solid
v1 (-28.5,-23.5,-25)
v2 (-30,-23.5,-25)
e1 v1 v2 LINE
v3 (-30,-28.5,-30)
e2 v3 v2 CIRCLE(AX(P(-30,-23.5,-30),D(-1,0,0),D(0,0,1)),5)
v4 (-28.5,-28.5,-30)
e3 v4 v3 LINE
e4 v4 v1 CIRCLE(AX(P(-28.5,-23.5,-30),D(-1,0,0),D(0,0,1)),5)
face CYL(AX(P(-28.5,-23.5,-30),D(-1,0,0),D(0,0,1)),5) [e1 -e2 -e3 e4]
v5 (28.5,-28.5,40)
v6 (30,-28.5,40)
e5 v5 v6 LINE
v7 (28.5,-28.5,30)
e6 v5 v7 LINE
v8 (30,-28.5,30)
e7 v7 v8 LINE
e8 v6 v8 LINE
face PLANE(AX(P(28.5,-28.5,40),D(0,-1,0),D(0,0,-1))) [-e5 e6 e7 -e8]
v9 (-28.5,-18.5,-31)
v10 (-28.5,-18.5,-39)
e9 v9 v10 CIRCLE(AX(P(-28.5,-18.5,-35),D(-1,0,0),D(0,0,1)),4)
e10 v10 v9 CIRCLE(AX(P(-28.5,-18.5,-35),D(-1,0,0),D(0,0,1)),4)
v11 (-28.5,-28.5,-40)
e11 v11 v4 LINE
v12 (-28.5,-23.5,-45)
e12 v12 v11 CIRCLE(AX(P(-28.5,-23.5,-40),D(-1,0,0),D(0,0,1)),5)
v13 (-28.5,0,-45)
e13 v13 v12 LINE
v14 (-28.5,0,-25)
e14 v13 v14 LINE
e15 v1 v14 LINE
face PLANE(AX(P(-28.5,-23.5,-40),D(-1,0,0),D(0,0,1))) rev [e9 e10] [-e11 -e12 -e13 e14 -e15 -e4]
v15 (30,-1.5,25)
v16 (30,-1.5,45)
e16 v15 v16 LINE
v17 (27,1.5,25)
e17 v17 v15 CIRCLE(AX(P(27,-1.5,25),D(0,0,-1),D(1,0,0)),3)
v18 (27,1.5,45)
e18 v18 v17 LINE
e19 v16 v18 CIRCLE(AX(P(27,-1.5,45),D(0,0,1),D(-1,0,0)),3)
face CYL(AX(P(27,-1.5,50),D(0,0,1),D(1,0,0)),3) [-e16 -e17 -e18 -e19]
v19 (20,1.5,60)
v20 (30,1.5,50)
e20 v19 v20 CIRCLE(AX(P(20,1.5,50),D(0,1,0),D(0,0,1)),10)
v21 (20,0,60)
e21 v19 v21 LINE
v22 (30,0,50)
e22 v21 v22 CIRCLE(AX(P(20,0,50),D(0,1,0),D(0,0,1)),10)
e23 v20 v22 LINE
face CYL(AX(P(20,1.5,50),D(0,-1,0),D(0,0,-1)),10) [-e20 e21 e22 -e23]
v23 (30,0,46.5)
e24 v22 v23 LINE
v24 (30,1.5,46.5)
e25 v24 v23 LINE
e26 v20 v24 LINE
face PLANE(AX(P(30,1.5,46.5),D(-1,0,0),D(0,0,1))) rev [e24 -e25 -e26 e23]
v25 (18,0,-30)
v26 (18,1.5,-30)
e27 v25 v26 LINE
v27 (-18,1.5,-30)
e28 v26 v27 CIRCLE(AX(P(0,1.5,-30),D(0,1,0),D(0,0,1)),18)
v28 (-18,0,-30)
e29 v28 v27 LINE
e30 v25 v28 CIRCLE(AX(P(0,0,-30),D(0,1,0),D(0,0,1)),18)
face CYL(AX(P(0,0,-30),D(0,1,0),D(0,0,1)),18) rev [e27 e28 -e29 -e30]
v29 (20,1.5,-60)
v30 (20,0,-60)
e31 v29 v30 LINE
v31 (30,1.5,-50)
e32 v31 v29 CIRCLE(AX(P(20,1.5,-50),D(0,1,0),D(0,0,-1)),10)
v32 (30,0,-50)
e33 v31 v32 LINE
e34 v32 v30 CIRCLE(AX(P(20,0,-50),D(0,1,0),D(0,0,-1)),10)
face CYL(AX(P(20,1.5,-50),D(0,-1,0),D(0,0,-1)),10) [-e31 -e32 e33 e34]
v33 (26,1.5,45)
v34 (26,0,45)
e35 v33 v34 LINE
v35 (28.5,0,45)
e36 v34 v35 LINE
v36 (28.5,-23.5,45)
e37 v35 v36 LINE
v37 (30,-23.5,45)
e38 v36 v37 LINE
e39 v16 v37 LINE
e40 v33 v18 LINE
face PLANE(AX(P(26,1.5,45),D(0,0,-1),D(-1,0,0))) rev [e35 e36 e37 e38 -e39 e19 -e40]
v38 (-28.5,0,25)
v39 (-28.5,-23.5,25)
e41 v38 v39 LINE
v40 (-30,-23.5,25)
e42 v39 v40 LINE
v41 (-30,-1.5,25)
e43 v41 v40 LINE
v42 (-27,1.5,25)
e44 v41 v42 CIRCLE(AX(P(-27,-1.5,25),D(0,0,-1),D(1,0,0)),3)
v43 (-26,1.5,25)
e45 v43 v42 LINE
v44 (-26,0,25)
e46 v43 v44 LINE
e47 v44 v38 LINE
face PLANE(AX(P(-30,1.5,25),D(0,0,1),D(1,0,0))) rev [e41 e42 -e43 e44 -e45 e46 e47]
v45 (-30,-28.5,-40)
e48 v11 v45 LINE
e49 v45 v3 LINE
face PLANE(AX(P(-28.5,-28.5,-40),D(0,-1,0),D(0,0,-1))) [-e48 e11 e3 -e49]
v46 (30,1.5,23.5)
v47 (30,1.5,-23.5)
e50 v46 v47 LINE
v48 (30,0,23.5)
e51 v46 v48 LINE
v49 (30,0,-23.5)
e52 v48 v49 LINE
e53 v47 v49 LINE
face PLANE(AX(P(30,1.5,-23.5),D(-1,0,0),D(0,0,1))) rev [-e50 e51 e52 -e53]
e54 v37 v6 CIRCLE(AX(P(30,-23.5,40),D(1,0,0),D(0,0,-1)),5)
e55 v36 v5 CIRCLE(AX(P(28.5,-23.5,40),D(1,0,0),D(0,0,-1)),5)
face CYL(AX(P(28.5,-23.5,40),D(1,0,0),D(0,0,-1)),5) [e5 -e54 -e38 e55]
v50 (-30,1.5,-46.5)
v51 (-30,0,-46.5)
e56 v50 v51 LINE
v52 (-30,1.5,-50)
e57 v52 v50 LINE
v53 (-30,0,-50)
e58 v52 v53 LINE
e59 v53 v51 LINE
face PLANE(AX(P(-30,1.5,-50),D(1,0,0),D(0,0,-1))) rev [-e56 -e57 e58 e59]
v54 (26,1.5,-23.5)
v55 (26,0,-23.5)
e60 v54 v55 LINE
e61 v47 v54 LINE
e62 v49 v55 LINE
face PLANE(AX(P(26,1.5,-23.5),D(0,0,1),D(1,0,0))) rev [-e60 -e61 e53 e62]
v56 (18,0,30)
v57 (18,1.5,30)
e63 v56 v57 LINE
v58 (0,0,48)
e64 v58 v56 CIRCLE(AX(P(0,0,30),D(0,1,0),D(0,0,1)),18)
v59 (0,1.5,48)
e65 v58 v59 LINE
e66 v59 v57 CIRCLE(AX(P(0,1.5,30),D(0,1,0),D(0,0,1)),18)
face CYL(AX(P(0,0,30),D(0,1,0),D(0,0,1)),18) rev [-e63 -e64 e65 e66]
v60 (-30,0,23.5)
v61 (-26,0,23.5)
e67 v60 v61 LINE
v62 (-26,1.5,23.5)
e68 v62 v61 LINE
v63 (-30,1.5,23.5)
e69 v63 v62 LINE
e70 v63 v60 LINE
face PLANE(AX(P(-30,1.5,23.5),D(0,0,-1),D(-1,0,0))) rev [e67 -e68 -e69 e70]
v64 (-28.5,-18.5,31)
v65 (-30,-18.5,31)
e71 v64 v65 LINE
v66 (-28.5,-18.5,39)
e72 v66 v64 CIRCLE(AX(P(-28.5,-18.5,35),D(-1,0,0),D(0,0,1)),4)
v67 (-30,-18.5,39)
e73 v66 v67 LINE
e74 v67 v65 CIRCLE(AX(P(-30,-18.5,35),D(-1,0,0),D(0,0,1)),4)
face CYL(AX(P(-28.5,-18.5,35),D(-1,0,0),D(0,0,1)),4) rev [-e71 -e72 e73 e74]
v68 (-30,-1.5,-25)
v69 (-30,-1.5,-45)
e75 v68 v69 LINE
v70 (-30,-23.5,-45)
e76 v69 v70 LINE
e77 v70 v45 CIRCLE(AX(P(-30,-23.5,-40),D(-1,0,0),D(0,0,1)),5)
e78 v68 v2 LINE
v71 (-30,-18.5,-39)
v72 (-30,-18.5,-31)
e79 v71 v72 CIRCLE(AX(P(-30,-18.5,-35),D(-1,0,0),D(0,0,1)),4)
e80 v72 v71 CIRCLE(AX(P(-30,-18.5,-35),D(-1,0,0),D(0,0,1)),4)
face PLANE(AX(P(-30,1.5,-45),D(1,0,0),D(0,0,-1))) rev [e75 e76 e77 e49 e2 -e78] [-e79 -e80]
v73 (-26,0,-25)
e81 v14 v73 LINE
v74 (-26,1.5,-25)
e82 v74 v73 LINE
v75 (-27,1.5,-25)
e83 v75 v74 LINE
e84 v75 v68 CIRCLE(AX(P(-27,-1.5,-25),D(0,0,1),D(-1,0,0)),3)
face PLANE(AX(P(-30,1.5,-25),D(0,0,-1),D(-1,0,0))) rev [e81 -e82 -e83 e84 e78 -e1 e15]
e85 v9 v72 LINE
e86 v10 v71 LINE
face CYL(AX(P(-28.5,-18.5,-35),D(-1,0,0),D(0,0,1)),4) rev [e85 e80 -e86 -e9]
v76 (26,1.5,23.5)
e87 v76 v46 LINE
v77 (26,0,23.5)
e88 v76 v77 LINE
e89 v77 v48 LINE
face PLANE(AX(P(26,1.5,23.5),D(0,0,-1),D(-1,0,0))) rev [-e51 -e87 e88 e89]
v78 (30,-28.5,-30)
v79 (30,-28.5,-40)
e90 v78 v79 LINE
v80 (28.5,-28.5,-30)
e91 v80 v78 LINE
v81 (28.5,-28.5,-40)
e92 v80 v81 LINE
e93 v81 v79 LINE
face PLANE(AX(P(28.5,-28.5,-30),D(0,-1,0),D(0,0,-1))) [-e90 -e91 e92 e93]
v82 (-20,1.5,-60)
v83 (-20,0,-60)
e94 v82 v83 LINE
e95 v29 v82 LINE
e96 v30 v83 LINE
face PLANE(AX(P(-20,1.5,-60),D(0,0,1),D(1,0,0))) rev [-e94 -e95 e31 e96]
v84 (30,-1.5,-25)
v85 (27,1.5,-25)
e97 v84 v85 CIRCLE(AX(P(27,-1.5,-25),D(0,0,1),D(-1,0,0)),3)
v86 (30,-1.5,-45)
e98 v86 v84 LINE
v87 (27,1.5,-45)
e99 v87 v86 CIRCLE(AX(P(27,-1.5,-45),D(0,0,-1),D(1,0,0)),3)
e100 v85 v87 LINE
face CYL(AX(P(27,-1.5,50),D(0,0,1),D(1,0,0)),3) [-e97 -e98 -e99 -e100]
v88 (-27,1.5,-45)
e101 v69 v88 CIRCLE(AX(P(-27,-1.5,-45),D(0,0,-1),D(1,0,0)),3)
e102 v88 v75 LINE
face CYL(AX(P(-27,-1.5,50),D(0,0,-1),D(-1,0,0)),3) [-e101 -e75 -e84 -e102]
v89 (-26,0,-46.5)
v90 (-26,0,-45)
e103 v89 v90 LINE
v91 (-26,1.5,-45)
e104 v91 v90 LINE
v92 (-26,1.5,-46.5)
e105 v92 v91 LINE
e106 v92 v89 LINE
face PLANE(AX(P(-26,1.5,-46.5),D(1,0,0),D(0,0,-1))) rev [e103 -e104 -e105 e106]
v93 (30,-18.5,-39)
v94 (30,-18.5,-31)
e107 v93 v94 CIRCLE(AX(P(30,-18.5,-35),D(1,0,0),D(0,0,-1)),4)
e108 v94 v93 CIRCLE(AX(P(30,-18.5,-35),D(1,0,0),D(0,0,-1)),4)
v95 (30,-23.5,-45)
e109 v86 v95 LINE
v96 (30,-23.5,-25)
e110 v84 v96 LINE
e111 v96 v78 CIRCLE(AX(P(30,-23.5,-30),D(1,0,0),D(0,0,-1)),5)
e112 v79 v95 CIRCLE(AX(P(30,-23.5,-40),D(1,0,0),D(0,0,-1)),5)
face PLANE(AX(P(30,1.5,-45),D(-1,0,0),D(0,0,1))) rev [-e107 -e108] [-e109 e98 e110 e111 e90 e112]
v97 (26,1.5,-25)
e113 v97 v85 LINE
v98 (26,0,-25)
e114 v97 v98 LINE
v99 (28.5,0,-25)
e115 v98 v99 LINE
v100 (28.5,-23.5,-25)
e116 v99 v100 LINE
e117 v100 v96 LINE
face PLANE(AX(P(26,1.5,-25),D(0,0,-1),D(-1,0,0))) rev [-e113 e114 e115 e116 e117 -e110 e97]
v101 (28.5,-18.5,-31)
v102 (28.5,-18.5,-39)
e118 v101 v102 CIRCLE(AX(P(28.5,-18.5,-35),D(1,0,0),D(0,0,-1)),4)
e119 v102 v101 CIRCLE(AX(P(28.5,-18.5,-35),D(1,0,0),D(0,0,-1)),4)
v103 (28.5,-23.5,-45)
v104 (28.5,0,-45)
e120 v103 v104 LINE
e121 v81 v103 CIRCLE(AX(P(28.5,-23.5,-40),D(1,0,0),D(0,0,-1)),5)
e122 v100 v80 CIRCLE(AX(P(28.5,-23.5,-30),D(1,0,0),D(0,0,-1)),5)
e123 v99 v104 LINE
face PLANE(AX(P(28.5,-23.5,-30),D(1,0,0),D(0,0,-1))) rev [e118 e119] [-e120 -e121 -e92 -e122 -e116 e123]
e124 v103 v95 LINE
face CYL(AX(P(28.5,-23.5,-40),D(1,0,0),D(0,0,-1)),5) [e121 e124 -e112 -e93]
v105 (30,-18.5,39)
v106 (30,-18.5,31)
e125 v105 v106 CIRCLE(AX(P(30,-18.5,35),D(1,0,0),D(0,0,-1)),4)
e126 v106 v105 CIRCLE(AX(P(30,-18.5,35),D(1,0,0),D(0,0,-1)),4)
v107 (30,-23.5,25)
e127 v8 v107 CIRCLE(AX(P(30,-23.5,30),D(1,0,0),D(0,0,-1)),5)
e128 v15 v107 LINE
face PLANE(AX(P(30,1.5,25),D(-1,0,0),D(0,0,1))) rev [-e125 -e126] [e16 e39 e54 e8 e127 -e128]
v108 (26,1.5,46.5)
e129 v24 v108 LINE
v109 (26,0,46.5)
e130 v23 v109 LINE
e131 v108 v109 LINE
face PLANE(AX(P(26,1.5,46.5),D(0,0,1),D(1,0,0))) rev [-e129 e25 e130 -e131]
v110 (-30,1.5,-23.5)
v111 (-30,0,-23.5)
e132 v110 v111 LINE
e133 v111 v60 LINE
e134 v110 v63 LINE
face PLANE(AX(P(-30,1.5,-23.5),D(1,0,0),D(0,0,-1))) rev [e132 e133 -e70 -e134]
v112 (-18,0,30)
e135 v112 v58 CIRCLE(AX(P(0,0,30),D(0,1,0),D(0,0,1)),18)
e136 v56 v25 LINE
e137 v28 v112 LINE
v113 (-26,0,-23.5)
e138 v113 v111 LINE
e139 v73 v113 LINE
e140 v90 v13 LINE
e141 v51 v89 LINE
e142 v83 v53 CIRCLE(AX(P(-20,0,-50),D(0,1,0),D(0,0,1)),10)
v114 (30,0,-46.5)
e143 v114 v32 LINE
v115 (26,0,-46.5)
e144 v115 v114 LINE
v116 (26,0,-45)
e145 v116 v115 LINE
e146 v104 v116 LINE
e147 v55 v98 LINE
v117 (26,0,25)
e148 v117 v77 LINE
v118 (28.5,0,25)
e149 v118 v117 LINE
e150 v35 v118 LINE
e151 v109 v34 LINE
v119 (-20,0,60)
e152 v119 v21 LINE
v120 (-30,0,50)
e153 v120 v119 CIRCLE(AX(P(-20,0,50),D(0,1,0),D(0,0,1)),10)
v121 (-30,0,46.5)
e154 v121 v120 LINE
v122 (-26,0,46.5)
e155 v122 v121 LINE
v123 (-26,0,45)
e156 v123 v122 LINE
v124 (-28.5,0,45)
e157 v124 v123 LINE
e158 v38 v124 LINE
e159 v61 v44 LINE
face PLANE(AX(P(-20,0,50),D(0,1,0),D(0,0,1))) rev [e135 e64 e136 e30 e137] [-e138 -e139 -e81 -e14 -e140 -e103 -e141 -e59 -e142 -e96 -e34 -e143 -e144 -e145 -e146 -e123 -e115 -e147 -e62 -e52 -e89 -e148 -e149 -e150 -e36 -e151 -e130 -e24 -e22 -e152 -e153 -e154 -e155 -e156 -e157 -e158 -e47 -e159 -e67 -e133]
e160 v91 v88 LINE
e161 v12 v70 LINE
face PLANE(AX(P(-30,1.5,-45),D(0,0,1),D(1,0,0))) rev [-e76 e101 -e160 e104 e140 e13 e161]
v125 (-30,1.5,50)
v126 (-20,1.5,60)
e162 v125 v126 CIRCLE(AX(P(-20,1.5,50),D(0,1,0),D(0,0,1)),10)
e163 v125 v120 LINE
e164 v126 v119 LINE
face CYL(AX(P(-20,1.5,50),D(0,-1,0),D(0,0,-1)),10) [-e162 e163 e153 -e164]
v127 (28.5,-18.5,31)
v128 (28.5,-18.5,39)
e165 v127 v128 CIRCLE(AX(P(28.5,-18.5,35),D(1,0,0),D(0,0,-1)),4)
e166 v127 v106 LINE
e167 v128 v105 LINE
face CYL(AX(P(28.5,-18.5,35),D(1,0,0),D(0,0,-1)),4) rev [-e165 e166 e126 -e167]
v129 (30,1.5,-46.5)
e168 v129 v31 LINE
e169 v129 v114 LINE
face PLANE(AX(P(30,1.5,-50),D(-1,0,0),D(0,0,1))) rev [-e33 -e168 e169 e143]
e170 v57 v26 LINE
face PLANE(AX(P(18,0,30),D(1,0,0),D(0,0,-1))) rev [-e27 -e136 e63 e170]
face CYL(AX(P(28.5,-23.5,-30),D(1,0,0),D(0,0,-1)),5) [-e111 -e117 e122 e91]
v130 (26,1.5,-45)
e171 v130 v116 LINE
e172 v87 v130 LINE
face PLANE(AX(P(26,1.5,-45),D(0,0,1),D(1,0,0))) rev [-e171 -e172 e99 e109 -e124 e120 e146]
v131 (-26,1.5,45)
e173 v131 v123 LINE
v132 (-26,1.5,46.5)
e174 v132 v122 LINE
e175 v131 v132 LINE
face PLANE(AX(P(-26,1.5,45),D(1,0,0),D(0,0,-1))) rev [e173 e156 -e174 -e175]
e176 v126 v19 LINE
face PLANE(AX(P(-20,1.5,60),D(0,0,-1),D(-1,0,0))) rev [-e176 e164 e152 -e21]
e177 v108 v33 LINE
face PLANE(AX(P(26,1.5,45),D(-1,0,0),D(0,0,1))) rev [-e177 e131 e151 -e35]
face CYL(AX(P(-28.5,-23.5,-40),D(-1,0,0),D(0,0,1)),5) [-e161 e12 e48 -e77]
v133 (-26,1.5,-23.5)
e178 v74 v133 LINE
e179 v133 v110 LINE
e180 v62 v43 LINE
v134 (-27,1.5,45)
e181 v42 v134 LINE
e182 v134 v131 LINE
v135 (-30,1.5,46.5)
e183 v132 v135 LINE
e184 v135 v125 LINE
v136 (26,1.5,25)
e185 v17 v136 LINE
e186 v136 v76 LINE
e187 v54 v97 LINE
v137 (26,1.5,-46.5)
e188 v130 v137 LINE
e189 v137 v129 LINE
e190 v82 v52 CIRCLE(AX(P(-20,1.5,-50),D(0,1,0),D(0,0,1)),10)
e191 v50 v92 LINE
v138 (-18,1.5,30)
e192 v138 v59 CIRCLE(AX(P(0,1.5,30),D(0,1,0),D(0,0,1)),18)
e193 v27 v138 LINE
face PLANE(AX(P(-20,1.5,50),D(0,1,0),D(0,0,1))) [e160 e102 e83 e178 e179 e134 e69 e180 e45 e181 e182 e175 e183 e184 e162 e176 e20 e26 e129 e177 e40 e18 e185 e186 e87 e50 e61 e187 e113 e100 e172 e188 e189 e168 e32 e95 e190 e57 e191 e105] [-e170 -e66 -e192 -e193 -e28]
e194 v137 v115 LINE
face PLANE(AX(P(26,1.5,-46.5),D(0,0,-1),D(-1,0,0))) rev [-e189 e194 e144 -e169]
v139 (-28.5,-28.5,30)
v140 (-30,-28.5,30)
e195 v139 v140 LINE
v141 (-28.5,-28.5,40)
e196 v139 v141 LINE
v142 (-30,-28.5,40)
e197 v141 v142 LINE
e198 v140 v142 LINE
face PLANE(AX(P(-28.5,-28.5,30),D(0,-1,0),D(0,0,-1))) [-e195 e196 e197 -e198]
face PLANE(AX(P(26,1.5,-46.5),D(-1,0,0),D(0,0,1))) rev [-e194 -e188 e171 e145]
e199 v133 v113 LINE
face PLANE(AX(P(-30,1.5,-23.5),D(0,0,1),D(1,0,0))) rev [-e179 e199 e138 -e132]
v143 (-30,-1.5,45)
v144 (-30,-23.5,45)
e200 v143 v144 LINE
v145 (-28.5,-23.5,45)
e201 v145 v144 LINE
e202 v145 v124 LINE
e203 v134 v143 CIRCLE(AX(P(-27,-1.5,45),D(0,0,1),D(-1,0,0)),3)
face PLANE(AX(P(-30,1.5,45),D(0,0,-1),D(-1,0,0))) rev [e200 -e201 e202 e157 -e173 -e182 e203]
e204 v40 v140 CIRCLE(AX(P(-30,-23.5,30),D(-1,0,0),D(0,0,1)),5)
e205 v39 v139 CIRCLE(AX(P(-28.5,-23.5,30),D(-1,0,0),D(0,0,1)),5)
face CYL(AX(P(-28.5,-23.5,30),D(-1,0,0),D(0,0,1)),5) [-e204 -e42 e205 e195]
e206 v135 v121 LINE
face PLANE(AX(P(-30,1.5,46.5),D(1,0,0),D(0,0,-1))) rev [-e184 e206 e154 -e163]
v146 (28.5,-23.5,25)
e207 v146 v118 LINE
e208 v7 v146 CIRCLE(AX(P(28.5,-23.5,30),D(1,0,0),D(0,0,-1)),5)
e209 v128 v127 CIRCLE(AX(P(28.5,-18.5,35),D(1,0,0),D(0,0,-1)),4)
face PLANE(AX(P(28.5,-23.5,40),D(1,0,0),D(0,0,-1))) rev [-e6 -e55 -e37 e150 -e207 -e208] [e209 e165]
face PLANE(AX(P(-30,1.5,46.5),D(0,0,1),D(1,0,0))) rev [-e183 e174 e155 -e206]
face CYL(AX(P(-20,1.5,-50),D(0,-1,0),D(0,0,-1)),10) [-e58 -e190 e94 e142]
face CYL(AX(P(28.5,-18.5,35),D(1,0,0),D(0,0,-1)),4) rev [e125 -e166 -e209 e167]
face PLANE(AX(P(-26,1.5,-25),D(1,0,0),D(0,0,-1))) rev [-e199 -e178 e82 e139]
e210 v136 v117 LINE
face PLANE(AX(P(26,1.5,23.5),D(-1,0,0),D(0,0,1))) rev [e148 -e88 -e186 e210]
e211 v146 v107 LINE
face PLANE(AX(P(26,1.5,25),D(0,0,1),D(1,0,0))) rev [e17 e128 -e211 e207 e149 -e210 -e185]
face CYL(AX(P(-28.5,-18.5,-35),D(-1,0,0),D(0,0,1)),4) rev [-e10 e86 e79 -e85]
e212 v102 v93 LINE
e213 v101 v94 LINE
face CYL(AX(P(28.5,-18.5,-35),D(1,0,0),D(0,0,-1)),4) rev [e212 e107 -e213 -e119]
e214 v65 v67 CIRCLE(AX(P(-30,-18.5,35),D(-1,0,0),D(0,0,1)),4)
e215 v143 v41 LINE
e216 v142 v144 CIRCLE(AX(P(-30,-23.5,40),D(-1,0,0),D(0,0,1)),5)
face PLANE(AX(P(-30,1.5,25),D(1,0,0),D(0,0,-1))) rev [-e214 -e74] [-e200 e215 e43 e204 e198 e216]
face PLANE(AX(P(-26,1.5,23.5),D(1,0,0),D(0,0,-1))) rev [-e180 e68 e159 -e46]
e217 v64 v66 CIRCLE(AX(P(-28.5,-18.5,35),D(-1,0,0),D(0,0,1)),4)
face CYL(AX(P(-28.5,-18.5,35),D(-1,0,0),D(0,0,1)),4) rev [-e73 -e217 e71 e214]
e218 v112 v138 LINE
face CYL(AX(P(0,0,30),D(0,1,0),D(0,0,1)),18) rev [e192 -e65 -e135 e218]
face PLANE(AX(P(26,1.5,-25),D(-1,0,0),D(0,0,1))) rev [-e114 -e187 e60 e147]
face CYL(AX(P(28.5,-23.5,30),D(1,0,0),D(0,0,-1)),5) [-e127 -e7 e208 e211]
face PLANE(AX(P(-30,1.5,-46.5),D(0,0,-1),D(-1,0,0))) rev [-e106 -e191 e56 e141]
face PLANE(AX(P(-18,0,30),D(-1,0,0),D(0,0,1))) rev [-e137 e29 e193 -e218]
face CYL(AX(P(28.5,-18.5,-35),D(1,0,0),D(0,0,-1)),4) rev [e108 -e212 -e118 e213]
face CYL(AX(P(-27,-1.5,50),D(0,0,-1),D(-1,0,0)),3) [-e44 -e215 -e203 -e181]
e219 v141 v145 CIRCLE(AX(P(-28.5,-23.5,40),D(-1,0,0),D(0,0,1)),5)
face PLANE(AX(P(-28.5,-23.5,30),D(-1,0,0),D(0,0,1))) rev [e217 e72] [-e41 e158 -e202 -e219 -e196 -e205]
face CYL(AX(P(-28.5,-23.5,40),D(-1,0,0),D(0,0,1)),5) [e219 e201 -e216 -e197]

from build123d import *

# Parameters (mm, degrees)
COVER_PLATE_1_5MM_DEPTH    = 1.5
SIDE_A_LEGS_SKETCH_R       = 4
SIDE_A_MOUNTING_LEGS_DEPTH = 1.5
SIDE_START                 = -1.5
SIDE_B_LEGS_SKETCH_R       = 4
SIDE_B_MOUNTING_LEGS_DEPTH = 1.5
CORNER_FILLETS_R3_R        = 3
OBLONG_SLOT_CUT_DEPTH      = 1.5


with BuildPart() as part:
    # Cover Plate Sketch → Cover Plate 1.5mm (new body)
    with BuildSketch(Plane(origin=(0, 0, 0), x_dir=(1, 0, 0), z_dir=(0, 1, 0))):
        with BuildLine():
            Line((-30, 45), (-26, 45))
            Line((-26, 45), (-26, 46.5))
            Line((-26, 46.5), (-30, 46.5))
            Line((-30, 46.5), (-30, 50))
            ThreePointArc((-30, 50), (-27.071067812, 57.071067812), (-20, 60))
            Line((-20, 60), (20, 60))
            ThreePointArc((20, 60), (27.071067812, 57.071067812), (30, 50))
            Line((30, 50), (30, 46.5))
            Line((30, 46.5), (26, 46.5))
            Line((26, 46.5), (26, 45))
            Line((26, 45), (30, 45))
            Line((30, 45), (30, 25))
            Line((30, 25), (26, 25))
            Line((26, 25), (26, 23.5))
            Line((26, 23.5), (30, 23.5))
            Line((30, 23.5), (30, -23.5))
            Line((30, -23.5), (26, -23.5))
            Line((26, -23.5), (26, -25))
            Line((26, -25), (30, -25))
            Line((30, -25), (30, -45))
            Line((30, -45), (26, -45))
            Line((26, -45), (26, -46.5))
            Line((26, -46.5), (30, -46.5))
            Line((30, -46.5), (30, -50))
            ThreePointArc((30, -50), (27.071067812, -57.071067812), (20, -60))
            Line((20, -60), (-20, -60))
            ThreePointArc((-20, -60), (-27.071067812, -57.071067812), (-30, -50))
            Line((-30, -50), (-30, -46.5))
            Line((-30, -46.5), (-26, -46.5))
            Line((-26, -46.5), (-26, -45))
            Line((-26, -45), (-30, -45))
            Line((-30, -45), (-30, -25))
            Line((-30, -25), (-26, -25))
            Line((-26, -25), (-26, -23.5))
            Line((-26, -23.5), (-30, -23.5))
            Line((-30, -23.5), (-30, 23.5))
            Line((-30, 23.5), (-26, 23.5))
            Line((-26, 23.5), (-26, 25))
            Line((-26, 25), (-30, 25))
            Line((-30, 25), (-30, 45))
        make_face()
    extrude(amount=COVER_PLATE_1_5MM_DEPTH)

    # Side A Legs Sketch → Side A Mounting Legs (add)
    # profile 1 of 2: a face of its own
    with BuildSketch(Plane(origin=(30, 0, 0), x_dir=(0, 0, -1), z_dir=(1, 0, 0))):
        with BuildLine():
            Line((-45, 1.5), (-25, 1.5))
            Line((-25, 1.5), (-25, -23.5))
            ThreePointArc((-25, -23.5), (-26.464466094, -27.035533906), (-30, -28.5))
            Line((-30, -28.5), (-40, -28.5))
            ThreePointArc((-40, -28.5), (-43.535533906, -27.035533906), (-45, -23.5))
            Line((-45, -23.5), (-45, 1.5))
        make_face()
        with Locations((-35, -18.5)):
            Circle(SIDE_A_LEGS_SKETCH_R, mode=Mode.SUBTRACT)
    # profile 2 of 2: a face of its own
    with BuildSketch(Plane(origin=(30, 0, 0), x_dir=(0, 0, -1), z_dir=(1, 0, 0))):
        with BuildLine():
            Line((25, 1.5), (45, 1.5))
            Line((45, 1.5), (45, -23.5))
            ThreePointArc((45, -23.5), (43.535533906, -27.035533906), (40, -28.5))
            Line((40, -28.5), (30, -28.5))
            ThreePointArc((30, -28.5), (26.464466094, -27.035533906), (25, -23.5))
            Line((25, -23.5), (25, 1.5))
        make_face()
        with Locations((35, -18.5)):
            Circle(SIDE_A_LEGS_SKETCH_R, mode=Mode.SUBTRACT)
    extrude(amount=-SIDE_A_MOUNTING_LEGS_DEPTH)

    # Side B Legs Sketch → Side B Mounting Legs (add)
    # profile 1 of 2: a face of its own
    with BuildSketch(Plane.ZY.offset(30).offset(SIDE_START)):
        with BuildLine():
            Line((-45, 1.5), (-25, 1.5))
            Line((-25, 1.5), (-25, -23.5))
            ThreePointArc((-25, -23.5), (-26.464466094, -27.035533906), (-30, -28.5))
            Line((-30, -28.5), (-40, -28.5))
            ThreePointArc((-40, -28.5), (-43.535533906, -27.035533906), (-45, -23.5))
            Line((-45, -23.5), (-45, 1.5))
        make_face()
        with Locations(Location((-35, -18.5, 0), (0, 0, 180))):
            Circle(SIDE_B_LEGS_SKETCH_R, mode=Mode.SUBTRACT)
    # profile 2 of 2: a face of its own
    with BuildSketch(Plane.ZY.offset(30).offset(SIDE_START)):
        with BuildLine():
            Line((25, 1.5), (45, 1.5))
            Line((45, 1.5), (45, -23.5))
            ThreePointArc((45, -23.5), (43.535533906, -27.035533906), (40, -28.5))
            Line((40, -28.5), (30, -28.5))
            ThreePointArc((30, -28.5), (26.464466094, -27.035533906), (25, -23.5))
            Line((25, -23.5), (25, 1.5))
        make_face()
        with Locations(Location((35, -18.5, 0), (0, 0, 180))):
            Circle(SIDE_B_LEGS_SKETCH_R, mode=Mode.SUBTRACT)
    extrude(amount=SIDE_B_MOUNTING_LEGS_DEPTH)

    # Corner Fillets R3
    corner_fillets_r3_edges = [part.edges().sort_by_distance(p)[0] for p in [
        (-30, 1.5, -35),
        (-30, 1.5, 35),
        (30, 1.5, 35),
        (30, 1.5, -35),
    ]]
    fillet(corner_fillets_r3_edges, radius=CORNER_FILLETS_R3_R)

    # Oblong Slot Sketch → Oblong Slot Cut (cut)
    with BuildSketch(Plane(origin=(0, 1.5, 0), x_dir=(1, 0, 0), z_dir=(0, 1, 0))):
        with BuildLine():
            Line((-18, -30), (-18, 30))
            ThreePointArc((-18, 30), (0, 48), (18, 30))
            Line((18, 30), (18, -30))
            ThreePointArc((18, -30), (0, -48), (-18, -30))
        make_face()
    extrude(amount=-OBLONG_SLOT_CUT_DEPTH, mode=Mode.SUBTRACT)


solid = part.part
